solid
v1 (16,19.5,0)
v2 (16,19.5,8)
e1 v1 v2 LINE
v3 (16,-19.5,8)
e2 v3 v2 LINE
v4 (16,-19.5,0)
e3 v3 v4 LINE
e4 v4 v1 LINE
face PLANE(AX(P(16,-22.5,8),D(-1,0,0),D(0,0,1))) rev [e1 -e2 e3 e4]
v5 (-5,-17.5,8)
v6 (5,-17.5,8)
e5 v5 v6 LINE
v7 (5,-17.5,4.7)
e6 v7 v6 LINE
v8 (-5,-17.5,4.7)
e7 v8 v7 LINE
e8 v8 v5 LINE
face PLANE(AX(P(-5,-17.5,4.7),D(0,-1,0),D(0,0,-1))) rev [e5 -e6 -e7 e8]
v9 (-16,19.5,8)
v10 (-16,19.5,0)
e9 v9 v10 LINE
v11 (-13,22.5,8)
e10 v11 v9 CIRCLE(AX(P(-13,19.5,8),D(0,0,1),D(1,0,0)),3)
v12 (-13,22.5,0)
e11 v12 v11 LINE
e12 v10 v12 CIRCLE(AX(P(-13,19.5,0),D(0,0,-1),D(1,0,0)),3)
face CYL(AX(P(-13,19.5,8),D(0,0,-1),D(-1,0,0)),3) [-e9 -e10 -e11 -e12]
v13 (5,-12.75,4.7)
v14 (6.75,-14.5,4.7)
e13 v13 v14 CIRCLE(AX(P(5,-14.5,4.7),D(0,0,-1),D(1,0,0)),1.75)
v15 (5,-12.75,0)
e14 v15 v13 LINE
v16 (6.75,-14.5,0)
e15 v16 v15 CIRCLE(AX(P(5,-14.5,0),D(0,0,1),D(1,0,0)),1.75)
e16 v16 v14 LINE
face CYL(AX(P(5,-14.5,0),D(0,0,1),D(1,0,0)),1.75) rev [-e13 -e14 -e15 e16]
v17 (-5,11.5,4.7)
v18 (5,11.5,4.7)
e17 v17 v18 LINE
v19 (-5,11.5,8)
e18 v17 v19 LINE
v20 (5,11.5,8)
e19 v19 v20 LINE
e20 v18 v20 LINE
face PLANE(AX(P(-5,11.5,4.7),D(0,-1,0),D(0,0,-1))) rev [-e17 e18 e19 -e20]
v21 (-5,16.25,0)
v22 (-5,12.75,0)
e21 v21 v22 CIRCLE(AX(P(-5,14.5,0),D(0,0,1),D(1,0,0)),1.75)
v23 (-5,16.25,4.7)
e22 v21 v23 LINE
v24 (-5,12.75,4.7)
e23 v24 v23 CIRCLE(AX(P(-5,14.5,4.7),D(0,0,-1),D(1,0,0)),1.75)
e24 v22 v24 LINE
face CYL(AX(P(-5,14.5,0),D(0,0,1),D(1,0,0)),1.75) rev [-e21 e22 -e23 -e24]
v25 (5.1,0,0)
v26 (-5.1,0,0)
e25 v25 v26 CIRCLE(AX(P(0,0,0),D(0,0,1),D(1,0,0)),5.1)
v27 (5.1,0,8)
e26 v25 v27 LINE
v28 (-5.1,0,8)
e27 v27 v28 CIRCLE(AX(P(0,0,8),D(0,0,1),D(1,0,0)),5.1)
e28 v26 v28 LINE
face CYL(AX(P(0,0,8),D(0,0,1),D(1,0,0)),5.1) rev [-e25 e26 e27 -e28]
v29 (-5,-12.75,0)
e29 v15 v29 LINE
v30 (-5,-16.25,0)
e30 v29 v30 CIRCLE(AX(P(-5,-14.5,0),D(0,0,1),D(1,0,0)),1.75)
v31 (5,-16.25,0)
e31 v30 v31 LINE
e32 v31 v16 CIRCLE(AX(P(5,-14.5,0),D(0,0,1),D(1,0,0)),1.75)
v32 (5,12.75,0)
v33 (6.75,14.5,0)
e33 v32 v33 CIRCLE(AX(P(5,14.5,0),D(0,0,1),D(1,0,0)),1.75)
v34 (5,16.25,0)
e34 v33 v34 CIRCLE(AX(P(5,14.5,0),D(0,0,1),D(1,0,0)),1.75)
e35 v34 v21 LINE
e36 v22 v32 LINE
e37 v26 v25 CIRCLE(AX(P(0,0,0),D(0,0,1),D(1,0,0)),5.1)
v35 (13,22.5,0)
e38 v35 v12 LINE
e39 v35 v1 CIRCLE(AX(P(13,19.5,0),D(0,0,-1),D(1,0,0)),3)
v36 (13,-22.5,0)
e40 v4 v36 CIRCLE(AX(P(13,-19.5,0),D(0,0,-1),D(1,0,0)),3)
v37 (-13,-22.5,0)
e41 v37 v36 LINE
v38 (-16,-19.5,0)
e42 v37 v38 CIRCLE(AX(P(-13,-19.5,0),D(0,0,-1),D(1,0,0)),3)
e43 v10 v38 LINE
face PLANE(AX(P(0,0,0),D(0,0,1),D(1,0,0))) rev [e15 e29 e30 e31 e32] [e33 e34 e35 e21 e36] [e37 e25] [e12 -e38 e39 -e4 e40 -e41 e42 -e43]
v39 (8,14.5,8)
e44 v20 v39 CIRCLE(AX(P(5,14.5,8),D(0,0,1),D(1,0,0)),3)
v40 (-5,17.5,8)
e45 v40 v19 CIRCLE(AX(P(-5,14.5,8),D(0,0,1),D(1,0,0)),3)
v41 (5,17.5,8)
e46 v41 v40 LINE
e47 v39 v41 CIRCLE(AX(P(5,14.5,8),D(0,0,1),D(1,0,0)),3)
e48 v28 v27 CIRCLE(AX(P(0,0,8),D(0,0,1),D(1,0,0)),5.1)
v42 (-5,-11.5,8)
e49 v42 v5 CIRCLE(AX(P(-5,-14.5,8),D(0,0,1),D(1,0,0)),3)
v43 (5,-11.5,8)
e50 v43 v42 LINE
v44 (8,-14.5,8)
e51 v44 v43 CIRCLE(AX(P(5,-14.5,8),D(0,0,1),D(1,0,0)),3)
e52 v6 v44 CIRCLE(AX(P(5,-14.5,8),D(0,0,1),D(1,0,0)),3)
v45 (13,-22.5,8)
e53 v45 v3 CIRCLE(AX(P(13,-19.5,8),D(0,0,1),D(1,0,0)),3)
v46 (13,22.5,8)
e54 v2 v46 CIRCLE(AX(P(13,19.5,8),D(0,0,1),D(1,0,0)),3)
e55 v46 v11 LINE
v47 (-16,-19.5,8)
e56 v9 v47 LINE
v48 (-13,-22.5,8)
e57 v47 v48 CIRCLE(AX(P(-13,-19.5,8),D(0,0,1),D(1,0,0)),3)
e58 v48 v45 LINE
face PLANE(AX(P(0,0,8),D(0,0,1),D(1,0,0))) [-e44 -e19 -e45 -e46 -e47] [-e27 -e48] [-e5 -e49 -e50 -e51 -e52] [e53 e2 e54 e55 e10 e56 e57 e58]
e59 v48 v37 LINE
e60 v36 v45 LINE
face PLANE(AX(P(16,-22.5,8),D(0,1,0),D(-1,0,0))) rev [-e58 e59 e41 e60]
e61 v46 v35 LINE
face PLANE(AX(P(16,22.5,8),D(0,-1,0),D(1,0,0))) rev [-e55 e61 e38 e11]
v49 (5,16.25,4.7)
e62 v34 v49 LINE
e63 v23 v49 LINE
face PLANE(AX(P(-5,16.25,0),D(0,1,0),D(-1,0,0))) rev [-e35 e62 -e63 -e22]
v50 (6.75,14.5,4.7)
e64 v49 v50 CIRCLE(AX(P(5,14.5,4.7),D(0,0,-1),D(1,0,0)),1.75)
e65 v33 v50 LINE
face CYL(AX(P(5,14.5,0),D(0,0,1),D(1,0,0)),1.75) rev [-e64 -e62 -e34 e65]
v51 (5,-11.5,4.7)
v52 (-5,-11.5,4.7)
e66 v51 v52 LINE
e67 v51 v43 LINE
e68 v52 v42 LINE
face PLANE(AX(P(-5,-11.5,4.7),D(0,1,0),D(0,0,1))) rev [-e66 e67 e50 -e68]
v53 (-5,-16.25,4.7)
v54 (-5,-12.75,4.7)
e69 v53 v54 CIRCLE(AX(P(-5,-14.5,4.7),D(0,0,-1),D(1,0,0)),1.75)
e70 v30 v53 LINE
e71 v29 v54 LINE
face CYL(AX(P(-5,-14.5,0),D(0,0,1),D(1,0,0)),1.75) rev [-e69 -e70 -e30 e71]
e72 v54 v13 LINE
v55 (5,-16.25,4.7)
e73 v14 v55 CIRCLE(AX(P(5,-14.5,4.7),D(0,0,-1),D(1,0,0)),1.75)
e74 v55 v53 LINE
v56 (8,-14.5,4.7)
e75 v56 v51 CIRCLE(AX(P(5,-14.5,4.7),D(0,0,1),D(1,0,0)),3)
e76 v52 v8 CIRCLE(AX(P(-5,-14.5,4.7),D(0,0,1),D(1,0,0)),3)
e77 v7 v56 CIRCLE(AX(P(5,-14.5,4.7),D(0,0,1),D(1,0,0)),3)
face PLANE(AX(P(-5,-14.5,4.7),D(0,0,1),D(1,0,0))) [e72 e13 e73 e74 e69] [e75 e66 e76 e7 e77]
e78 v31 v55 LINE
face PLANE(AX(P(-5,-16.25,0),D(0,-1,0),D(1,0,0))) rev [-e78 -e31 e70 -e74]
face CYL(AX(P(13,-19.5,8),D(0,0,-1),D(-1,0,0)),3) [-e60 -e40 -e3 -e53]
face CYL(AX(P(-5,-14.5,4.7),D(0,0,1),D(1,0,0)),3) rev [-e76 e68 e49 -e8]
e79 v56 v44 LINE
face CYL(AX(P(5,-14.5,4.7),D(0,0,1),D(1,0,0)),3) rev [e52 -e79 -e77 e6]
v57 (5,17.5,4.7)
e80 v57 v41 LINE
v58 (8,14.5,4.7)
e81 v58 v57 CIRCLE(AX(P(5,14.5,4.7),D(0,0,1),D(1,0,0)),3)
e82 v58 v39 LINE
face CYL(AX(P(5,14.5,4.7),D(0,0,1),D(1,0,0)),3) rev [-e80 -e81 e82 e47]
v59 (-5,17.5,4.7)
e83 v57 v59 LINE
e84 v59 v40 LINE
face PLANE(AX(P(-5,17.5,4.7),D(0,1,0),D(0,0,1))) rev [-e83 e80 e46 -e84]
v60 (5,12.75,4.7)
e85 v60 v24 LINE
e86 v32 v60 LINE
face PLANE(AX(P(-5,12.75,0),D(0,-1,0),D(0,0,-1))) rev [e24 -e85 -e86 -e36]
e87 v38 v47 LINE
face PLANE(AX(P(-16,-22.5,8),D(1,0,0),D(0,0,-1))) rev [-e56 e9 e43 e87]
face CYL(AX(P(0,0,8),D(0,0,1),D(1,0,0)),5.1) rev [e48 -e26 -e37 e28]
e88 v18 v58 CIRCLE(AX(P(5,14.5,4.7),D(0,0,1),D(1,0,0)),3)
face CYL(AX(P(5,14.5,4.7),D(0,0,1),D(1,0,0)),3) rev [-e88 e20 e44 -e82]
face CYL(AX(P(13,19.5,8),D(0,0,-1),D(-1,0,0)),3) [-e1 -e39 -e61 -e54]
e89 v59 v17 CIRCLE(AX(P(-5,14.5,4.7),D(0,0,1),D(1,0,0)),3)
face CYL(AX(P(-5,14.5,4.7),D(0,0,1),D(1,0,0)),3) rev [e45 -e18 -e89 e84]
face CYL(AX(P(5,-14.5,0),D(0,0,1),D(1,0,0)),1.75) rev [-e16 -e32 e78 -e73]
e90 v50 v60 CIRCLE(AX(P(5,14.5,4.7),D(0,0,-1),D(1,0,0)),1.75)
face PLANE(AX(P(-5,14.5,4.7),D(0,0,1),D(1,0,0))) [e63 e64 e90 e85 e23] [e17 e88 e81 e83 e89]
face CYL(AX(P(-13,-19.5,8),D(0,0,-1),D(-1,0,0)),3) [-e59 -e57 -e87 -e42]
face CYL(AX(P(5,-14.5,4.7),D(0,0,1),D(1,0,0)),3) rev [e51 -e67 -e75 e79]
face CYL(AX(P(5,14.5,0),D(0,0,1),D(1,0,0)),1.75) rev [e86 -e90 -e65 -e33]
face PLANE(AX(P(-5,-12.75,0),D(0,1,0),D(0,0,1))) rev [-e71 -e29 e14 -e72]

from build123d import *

# Parameters (mm, degrees)
SKETCH1_W           = 32
SKETCH1_H           = 45
BOSS_EXTRUDE1_DEPTH = 8
M12_TAPPED_HOLE1_D  = 10.2
CUT_EXTRUDE1_DEPTH  = 29.744564704
CUT_EXTRUDE2_DEPTH  = 3.3
FILLET1_R           = 3


with BuildPart() as part:
    # Sketch1 → Boss-Extrude1 (new body)
    with BuildSketch(Plane.XY):
        Rectangle(SKETCH1_W, SKETCH1_H)
    extrude(amount=BOSS_EXTRUDE1_DEPTH)

    # M12 Tapped Hole1 (through all)
    with Locations(Plane.XY.offset(8)):
        with Locations((0, 0)):
            Hole(M12_TAPPED_HOLE1_D / 2)

    # Sketch5 → Cut-Extrude1 (cut, through all)
    with BuildSketch(Plane.XY.offset(8)):
        with BuildLine():
            Line((-5, -12.75), (5, -12.75))
            ThreePointArc((5, -12.75), (6.75, -14.5), (5, -16.25))
            Line((5, -16.25), (-5, -16.25))
            ThreePointArc((-5, -16.25), (-6.75, -14.5), (-5, -12.75))
        make_face()
        with BuildLine():
            Line((-5, 16.25), (5, 16.25))
            ThreePointArc((5, 16.25), (6.75, 14.5), (5, 12.75))
            Line((5, 12.75), (-5, 12.75))
            ThreePointArc((-5, 12.75), (-6.75, 14.5), (-5, 16.25))
        make_face()
    extrude(amount=-CUT_EXTRUDE1_DEPTH, mode=Mode.SUBTRACT)

    # Sketch6 → Cut-Extrude2 (cut)
    with BuildSketch(Plane.XY.offset(8)):
        with BuildLine():
            Line((-5, -11.5), (5, -11.5))
            ThreePointArc((5, -11.5), (8, -14.5), (5, -17.5))
            Line((5, -17.5), (-5, -17.5))
            ThreePointArc((-5, -17.5), (-8, -14.5), (-5, -11.5))
        make_face()
        with BuildLine():
            Line((-5, 17.5), (5, 17.5))
            ThreePointArc((5, 17.5), (8, 14.5), (5, 11.5))
            Line((5, 11.5), (-5, 11.5))
            ThreePointArc((-5, 11.5), (-8, 14.5), (-5, 17.5))
        make_face()
    extrude(amount=-CUT_EXTRUDE2_DEPTH, mode=Mode.SUBTRACT)

    # Fillet1
    fillet1_edges = [part.edges().sort_by_distance(p)[0] for p in [
        (-16, 22.5, 4),
        (16, 22.5, 4),
        (16, -22.5, 4),
        (-16, -22.5, 4),
    ]]
    fillet(fillet1_edges, radius=FILLET1_R)


solid = part.part
